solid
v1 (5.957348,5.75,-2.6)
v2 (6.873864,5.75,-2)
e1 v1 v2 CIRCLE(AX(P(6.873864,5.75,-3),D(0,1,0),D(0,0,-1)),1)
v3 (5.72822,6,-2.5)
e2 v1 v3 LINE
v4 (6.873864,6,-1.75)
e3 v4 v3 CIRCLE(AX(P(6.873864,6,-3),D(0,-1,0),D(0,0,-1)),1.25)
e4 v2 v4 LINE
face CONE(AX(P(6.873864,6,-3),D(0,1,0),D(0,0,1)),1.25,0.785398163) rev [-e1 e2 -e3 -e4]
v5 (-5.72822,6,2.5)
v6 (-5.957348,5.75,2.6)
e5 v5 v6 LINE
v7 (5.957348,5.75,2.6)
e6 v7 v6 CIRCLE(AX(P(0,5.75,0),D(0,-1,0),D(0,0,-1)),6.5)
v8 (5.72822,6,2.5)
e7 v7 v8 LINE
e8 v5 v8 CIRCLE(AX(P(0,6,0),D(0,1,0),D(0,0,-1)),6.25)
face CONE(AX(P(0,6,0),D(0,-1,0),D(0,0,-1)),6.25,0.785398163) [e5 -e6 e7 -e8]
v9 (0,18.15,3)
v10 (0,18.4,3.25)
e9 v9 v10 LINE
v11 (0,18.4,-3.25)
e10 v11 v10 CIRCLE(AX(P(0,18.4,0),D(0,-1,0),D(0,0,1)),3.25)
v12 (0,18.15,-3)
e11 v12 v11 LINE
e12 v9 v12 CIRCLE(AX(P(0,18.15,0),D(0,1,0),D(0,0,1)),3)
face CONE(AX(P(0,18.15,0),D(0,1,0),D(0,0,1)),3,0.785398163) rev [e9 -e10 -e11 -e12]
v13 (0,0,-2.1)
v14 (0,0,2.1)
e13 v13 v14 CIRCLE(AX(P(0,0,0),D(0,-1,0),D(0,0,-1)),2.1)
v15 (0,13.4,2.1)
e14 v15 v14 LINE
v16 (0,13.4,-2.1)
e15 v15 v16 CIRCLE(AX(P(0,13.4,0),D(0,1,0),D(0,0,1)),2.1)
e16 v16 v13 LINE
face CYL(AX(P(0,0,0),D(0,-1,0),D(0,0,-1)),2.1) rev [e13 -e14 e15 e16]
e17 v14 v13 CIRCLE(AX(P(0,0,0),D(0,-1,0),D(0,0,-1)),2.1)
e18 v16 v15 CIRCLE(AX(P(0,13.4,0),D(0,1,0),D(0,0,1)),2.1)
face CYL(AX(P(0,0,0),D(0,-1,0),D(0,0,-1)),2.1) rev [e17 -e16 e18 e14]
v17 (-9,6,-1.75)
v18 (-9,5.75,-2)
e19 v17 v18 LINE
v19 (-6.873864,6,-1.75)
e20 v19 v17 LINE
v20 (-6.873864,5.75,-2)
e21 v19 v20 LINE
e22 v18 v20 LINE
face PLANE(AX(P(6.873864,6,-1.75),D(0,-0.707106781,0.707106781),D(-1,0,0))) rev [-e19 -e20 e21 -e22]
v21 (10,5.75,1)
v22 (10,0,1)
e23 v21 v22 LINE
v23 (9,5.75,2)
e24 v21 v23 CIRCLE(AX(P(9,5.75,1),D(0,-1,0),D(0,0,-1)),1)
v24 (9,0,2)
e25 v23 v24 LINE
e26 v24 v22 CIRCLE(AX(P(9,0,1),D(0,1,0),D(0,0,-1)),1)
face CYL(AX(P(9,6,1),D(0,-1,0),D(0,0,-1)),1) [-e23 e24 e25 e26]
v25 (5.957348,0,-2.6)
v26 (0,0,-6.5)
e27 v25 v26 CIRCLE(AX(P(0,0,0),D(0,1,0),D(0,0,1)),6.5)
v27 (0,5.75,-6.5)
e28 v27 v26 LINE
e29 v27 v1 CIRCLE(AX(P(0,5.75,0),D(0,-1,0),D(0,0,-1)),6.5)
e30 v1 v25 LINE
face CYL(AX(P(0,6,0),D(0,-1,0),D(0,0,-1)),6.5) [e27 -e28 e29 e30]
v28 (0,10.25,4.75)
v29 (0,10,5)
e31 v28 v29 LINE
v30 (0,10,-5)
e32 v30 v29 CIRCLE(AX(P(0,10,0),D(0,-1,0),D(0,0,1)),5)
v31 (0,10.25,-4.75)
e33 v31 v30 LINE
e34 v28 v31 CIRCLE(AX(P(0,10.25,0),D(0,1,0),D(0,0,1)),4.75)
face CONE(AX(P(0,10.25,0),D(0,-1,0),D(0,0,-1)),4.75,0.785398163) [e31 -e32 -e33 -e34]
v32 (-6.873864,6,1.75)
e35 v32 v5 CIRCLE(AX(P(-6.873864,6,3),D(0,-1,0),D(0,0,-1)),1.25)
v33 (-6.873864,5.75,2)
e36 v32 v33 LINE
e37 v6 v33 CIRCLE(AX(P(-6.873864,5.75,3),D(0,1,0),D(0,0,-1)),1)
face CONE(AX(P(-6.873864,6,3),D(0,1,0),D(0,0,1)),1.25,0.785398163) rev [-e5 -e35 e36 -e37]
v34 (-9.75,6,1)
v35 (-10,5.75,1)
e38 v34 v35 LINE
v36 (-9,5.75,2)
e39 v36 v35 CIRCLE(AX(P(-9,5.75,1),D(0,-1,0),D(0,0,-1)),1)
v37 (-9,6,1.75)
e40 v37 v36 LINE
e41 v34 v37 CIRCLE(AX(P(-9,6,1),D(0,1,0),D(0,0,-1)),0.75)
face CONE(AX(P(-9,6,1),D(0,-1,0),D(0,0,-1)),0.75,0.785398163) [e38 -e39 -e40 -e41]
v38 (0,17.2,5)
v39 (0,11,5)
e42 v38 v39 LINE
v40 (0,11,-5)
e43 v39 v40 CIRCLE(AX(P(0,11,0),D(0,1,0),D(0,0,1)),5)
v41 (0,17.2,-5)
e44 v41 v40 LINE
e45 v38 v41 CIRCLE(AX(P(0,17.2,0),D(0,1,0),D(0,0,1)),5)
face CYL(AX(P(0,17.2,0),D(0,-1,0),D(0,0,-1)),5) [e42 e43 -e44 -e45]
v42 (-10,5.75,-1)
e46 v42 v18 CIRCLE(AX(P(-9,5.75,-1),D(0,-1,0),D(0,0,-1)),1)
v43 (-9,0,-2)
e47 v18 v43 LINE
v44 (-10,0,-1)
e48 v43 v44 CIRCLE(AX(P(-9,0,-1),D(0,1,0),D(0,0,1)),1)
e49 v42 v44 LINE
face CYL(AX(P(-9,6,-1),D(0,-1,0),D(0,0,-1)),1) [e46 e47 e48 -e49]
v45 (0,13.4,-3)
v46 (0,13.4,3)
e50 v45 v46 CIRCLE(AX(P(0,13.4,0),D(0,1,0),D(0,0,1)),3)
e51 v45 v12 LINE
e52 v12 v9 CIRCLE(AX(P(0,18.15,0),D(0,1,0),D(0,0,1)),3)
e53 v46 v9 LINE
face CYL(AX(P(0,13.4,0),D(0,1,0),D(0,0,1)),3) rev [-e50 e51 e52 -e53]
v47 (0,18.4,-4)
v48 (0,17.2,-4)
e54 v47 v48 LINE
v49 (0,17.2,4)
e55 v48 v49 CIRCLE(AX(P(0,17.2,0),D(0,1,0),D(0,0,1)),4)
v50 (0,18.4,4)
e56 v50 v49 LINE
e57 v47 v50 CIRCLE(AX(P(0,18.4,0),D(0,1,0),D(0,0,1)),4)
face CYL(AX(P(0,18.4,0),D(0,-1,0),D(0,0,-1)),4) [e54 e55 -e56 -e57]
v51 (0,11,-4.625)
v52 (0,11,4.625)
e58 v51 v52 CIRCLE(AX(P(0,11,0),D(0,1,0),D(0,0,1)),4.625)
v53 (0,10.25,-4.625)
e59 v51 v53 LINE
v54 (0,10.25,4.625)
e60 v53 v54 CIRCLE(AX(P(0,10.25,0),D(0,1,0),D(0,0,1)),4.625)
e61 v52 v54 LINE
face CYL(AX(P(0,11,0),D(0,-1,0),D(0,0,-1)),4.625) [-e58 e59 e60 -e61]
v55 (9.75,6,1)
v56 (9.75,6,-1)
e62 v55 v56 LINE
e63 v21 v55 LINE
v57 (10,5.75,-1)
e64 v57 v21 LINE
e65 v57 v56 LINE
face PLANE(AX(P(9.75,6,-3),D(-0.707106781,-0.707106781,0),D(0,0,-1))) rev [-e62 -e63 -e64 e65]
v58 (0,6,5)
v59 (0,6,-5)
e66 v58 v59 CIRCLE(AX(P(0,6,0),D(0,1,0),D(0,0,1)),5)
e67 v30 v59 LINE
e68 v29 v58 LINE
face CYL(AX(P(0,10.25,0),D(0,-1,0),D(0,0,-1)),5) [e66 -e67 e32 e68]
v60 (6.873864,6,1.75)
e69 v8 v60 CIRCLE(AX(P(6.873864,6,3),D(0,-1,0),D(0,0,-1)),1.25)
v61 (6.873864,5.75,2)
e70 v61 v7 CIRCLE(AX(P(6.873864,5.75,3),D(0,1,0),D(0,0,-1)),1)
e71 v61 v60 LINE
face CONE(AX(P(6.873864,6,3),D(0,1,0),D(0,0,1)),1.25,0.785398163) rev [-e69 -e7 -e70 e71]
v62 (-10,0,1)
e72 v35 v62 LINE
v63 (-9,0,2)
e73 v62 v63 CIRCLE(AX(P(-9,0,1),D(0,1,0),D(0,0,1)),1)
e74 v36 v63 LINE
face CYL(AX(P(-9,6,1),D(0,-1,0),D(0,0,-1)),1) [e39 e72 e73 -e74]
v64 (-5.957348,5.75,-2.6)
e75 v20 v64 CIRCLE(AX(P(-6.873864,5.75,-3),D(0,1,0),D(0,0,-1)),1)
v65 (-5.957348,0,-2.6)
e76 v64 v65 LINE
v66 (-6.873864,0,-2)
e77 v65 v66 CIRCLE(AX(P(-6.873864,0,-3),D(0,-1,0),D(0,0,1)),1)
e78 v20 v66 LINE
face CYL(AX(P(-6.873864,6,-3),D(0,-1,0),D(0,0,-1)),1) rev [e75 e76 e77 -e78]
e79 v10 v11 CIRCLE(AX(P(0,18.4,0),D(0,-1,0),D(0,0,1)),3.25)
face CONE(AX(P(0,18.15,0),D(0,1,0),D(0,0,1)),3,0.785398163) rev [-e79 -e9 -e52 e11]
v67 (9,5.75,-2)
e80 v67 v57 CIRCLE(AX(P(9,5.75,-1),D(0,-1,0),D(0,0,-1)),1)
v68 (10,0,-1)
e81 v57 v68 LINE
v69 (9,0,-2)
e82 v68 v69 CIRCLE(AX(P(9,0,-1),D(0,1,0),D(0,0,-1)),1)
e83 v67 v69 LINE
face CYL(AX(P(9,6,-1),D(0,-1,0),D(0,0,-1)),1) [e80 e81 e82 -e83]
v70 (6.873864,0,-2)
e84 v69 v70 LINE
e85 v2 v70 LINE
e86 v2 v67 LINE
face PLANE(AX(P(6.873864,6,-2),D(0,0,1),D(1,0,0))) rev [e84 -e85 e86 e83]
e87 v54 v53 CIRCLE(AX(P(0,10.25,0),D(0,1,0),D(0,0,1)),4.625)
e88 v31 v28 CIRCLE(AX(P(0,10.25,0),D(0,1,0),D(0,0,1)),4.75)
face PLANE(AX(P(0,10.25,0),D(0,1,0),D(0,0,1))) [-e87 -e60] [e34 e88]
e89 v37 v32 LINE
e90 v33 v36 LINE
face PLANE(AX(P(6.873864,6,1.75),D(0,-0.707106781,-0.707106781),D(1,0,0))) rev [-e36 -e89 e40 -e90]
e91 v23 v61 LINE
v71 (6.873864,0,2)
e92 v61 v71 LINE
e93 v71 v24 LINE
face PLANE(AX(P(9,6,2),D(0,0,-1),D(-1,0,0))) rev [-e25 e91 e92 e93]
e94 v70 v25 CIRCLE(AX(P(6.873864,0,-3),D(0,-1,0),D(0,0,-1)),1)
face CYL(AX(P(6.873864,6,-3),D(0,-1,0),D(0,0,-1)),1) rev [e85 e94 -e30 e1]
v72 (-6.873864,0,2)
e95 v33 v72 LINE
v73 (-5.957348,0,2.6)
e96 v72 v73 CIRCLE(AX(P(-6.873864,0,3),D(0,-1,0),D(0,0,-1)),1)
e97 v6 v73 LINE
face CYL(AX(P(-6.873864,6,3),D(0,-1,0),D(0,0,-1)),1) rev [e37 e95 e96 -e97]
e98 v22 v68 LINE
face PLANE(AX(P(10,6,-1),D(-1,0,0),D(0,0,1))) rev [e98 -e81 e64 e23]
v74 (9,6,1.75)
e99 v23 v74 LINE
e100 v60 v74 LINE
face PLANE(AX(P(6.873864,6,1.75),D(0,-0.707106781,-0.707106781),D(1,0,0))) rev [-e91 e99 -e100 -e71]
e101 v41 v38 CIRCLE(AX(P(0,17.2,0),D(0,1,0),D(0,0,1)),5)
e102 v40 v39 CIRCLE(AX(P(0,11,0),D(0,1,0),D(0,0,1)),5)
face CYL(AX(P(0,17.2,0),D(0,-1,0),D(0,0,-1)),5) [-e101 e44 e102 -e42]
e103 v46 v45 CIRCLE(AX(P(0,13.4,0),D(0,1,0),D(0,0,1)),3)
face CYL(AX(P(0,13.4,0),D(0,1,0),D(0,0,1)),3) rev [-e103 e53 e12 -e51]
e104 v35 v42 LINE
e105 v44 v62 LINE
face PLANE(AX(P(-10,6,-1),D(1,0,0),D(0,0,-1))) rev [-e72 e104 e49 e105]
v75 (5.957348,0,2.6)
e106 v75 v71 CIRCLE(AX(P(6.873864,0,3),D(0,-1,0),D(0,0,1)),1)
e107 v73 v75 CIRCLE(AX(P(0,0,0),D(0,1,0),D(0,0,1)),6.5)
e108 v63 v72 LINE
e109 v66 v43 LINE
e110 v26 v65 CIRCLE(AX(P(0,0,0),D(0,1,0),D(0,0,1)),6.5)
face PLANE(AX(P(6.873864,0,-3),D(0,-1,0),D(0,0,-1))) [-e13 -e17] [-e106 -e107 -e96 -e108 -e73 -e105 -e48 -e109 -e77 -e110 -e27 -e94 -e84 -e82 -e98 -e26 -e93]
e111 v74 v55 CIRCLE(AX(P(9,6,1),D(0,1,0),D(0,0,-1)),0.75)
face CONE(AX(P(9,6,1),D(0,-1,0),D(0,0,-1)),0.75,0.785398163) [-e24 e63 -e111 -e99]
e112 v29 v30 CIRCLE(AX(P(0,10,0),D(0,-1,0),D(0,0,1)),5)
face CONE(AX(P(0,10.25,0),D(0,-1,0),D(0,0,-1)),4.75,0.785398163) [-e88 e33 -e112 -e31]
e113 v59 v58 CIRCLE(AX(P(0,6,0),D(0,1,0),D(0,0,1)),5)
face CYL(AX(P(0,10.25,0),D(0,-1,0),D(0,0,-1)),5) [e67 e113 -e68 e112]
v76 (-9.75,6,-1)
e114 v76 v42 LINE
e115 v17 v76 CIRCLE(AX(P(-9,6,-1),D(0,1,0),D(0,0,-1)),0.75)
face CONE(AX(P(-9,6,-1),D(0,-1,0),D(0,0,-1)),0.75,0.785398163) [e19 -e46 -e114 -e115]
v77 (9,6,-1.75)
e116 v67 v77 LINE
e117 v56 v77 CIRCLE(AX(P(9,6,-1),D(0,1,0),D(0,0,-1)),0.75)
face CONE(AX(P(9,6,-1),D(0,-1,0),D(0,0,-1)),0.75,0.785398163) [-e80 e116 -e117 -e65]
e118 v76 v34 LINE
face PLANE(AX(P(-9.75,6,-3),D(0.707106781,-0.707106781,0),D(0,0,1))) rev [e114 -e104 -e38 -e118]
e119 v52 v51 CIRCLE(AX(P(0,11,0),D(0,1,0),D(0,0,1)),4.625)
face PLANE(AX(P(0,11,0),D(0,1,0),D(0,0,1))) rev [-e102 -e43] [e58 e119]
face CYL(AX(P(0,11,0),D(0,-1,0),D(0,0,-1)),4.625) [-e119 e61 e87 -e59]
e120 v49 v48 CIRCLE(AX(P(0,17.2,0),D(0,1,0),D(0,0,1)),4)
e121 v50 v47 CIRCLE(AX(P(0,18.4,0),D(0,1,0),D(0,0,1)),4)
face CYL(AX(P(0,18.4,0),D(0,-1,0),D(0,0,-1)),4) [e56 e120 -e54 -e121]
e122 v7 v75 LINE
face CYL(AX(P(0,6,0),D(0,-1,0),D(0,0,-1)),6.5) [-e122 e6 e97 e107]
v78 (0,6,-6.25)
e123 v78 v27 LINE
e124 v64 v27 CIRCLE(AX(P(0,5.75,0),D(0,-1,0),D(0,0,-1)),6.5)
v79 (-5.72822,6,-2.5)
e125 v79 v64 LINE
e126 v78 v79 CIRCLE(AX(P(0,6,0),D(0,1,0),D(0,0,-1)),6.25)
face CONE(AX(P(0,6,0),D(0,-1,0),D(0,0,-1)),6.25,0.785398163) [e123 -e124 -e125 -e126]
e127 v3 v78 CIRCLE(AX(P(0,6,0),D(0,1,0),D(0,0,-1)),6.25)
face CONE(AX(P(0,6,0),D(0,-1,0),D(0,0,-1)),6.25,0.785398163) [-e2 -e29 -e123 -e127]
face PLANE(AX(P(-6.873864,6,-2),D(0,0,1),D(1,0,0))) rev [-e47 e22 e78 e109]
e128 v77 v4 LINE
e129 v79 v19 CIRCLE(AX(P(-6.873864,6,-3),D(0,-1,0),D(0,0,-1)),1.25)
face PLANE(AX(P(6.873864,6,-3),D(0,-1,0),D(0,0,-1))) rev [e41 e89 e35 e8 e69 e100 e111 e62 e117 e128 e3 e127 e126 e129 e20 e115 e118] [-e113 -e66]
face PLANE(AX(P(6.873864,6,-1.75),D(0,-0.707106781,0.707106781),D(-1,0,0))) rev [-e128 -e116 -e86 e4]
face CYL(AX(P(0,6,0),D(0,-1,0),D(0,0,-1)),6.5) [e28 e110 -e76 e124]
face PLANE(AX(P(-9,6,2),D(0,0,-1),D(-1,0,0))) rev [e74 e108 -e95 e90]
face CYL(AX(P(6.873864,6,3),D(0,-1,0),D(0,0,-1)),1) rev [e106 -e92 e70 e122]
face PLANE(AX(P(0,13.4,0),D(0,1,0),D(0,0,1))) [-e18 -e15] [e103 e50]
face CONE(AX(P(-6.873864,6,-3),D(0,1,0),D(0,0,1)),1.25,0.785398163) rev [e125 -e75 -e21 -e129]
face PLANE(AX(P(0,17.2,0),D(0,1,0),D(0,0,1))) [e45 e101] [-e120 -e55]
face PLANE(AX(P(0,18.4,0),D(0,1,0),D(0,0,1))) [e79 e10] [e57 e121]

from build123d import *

# Parameters (mm, degrees)
EXTRUDE_1_DEPTH      = 6
SKETCH_2_R           = 5
EXTRUDE_2_DEPTH      = 4.25
SKETCH_3_R           = 4.625
EXTRUDE_3_DEPTH      = 0.75
SKETCH_4_R           = 5
EXTRUDE_M10_1_DEPTH  = 6.2
SKETCH_5_R           = 4
EXTRUDE_5_DEPTH      = 1.2
SKETCH_6_R           = 3
CUT_EXTRUDE_1_DEPTH  = 5
HOLE_WIZARD_M5_1_D   = 4.2
CHAMFER_C0_25_1_SIZE = 0.25


with BuildPart() as part:
    # 草图1 → 凸台-拉伸1 (new body)
    with BuildSketch(Plane(origin=(0, 0, 0), x_dir=(1, 0, 0), z_dir=(0, 1, 0))):
        with BuildLine():
            Line((6.873863542, 2), (9, 2))
            ThreePointArc((9, 2), (9.707106781, 1.707106781), (10, 1))
            Line((10, 1), (10, -1))
            ThreePointArc((10, -1), (9.707106781, -1.707106781), (9, -2))
            Line((9, -2), (6.873863542, -2))
            ThreePointArc((6.873863542, -2), (6.326140985, -2.163339973), (5.957348403, -2.6))
            ThreePointArc((5.957348403, -2.6), (0, -6.5), (-5.957348403, -2.6))
            ThreePointArc((-5.957348403, -2.6), (-6.326140985, -2.163339973), (-6.873863542, -2))
            Line((-6.873863542, -2), (-9, -2))
            ThreePointArc((-9, -2), (-9.707106781, -1.707106781), (-10, -1))
            Line((-10, -1), (-10, 1))
            ThreePointArc((-10, 1), (-9.707106781, 1.707106781), (-9, 2))
            Line((-9, 2), (-6.873863542, 2))
            ThreePointArc((-6.873863542, 2), (-6.326140985, 2.163339973), (-5.957348403, 2.6))
            ThreePointArc((-5.957348403, 2.6), (0, 6.5), (5.957348403, 2.6))
            ThreePointArc((5.957348403, 2.6), (6.326140985, 2.163339973), (6.873863542, 2))
        make_face()
    extrude(amount=EXTRUDE_1_DEPTH)

    # 草图2 → 凸台-拉伸2 (add)
    with BuildSketch(Plane(origin=(0, 6, 0), x_dir=(1, 0, 0), z_dir=(0, 1, 0))):
        with Locations(Location((0, 0, 0), (0, 0, 270))):
            Circle(SKETCH_2_R)
    extrude(amount=EXTRUDE_2_DEPTH)

    # 草图3 → 凸台-拉伸3 (add)
    with BuildSketch(Plane(origin=(0, 10.25, 0), x_dir=(1, 0, 0), z_dir=(0, 1, 0))):
        with Locations(Location((0, 0, 0), (0, 0, 270))):
            Circle(SKETCH_3_R)
    extrude(amount=EXTRUDE_3_DEPTH)

    # 草图4 → M10×1 细牙螺柱 (add)
    with BuildSketch(Plane(origin=(0, 11, 0), x_dir=(1, 0, 0), z_dir=(0, 1, 0))):
        with Locations(Location((0, 0, 0), (0, 0, 270))):
            Circle(SKETCH_4_R)
    extrude(amount=EXTRUDE_M10_1_DEPTH)

    # 草图5 → 凸台-拉伸5 (add)
    with BuildSketch(Plane(origin=(0, 17.2, 0), x_dir=(1, 0, 0), z_dir=(0, 1, 0))):
        with Locations(Location((0, 0, 0), (0, 0, 270))):
            Circle(SKETCH_5_R)
    extrude(amount=EXTRUDE_5_DEPTH)

    # 草图6 → 切除-拉伸1 (cut)
    with BuildSketch(Plane(origin=(0, 18.4, 0), x_dir=(1, 0, 0), z_dir=(0, 1, 0))):
        with Locations(Location((0, 0, 0), (0, 0, 270))):
            Circle(SKETCH_6_R)
    extrude(amount=-CUT_EXTRUDE_1_DEPTH, mode=Mode.SUBTRACT)

    # M5 螺纹孔1 (through all)
    with Locations(Plane(origin=(0, 0, 0), x_dir=(-1, 0, 0), z_dir=(0, -1, 0))):
        with Locations((0, 0)):
            Hole(HOLE_WIZARD_M5_1_D / 2)

    # C0.25 倒角1
    chamfer_c0_25_1_edges = [part.edges().sort_by_distance(p)[0] for p in [
        (-6.326140985, 6, -2.163339973),
        (-7.936931771, 6, -2),
        (-9.707106781, 6, -1.707106781),
        (-10, 6, 0),
        (-9.707106781, 6, 1.707106781),
        (-7.936931771, 6, 2),
        (-6.326140985, 6, 2.163339973),
        (0, 6, 6.5),
        (6.326140985, 6, 2.163339973),
        (0, 10.25, -5),
        (7.936931771, 6, 2),
        (6.326140985, 6, -2.163339973),
        (9.707106781, 6, 1.707106781),
        (10, 6, 0),
        (9.707106781, 6, -1.707106781),
        (7.936931771, 6, -2),
        (0, 18.4, -3),
        (0, 6, -6.5),
    ]]
    chamfer(chamfer_c0_25_1_edges, length=CHAMFER_C0_25_1_SIZE)


solid = part.part
